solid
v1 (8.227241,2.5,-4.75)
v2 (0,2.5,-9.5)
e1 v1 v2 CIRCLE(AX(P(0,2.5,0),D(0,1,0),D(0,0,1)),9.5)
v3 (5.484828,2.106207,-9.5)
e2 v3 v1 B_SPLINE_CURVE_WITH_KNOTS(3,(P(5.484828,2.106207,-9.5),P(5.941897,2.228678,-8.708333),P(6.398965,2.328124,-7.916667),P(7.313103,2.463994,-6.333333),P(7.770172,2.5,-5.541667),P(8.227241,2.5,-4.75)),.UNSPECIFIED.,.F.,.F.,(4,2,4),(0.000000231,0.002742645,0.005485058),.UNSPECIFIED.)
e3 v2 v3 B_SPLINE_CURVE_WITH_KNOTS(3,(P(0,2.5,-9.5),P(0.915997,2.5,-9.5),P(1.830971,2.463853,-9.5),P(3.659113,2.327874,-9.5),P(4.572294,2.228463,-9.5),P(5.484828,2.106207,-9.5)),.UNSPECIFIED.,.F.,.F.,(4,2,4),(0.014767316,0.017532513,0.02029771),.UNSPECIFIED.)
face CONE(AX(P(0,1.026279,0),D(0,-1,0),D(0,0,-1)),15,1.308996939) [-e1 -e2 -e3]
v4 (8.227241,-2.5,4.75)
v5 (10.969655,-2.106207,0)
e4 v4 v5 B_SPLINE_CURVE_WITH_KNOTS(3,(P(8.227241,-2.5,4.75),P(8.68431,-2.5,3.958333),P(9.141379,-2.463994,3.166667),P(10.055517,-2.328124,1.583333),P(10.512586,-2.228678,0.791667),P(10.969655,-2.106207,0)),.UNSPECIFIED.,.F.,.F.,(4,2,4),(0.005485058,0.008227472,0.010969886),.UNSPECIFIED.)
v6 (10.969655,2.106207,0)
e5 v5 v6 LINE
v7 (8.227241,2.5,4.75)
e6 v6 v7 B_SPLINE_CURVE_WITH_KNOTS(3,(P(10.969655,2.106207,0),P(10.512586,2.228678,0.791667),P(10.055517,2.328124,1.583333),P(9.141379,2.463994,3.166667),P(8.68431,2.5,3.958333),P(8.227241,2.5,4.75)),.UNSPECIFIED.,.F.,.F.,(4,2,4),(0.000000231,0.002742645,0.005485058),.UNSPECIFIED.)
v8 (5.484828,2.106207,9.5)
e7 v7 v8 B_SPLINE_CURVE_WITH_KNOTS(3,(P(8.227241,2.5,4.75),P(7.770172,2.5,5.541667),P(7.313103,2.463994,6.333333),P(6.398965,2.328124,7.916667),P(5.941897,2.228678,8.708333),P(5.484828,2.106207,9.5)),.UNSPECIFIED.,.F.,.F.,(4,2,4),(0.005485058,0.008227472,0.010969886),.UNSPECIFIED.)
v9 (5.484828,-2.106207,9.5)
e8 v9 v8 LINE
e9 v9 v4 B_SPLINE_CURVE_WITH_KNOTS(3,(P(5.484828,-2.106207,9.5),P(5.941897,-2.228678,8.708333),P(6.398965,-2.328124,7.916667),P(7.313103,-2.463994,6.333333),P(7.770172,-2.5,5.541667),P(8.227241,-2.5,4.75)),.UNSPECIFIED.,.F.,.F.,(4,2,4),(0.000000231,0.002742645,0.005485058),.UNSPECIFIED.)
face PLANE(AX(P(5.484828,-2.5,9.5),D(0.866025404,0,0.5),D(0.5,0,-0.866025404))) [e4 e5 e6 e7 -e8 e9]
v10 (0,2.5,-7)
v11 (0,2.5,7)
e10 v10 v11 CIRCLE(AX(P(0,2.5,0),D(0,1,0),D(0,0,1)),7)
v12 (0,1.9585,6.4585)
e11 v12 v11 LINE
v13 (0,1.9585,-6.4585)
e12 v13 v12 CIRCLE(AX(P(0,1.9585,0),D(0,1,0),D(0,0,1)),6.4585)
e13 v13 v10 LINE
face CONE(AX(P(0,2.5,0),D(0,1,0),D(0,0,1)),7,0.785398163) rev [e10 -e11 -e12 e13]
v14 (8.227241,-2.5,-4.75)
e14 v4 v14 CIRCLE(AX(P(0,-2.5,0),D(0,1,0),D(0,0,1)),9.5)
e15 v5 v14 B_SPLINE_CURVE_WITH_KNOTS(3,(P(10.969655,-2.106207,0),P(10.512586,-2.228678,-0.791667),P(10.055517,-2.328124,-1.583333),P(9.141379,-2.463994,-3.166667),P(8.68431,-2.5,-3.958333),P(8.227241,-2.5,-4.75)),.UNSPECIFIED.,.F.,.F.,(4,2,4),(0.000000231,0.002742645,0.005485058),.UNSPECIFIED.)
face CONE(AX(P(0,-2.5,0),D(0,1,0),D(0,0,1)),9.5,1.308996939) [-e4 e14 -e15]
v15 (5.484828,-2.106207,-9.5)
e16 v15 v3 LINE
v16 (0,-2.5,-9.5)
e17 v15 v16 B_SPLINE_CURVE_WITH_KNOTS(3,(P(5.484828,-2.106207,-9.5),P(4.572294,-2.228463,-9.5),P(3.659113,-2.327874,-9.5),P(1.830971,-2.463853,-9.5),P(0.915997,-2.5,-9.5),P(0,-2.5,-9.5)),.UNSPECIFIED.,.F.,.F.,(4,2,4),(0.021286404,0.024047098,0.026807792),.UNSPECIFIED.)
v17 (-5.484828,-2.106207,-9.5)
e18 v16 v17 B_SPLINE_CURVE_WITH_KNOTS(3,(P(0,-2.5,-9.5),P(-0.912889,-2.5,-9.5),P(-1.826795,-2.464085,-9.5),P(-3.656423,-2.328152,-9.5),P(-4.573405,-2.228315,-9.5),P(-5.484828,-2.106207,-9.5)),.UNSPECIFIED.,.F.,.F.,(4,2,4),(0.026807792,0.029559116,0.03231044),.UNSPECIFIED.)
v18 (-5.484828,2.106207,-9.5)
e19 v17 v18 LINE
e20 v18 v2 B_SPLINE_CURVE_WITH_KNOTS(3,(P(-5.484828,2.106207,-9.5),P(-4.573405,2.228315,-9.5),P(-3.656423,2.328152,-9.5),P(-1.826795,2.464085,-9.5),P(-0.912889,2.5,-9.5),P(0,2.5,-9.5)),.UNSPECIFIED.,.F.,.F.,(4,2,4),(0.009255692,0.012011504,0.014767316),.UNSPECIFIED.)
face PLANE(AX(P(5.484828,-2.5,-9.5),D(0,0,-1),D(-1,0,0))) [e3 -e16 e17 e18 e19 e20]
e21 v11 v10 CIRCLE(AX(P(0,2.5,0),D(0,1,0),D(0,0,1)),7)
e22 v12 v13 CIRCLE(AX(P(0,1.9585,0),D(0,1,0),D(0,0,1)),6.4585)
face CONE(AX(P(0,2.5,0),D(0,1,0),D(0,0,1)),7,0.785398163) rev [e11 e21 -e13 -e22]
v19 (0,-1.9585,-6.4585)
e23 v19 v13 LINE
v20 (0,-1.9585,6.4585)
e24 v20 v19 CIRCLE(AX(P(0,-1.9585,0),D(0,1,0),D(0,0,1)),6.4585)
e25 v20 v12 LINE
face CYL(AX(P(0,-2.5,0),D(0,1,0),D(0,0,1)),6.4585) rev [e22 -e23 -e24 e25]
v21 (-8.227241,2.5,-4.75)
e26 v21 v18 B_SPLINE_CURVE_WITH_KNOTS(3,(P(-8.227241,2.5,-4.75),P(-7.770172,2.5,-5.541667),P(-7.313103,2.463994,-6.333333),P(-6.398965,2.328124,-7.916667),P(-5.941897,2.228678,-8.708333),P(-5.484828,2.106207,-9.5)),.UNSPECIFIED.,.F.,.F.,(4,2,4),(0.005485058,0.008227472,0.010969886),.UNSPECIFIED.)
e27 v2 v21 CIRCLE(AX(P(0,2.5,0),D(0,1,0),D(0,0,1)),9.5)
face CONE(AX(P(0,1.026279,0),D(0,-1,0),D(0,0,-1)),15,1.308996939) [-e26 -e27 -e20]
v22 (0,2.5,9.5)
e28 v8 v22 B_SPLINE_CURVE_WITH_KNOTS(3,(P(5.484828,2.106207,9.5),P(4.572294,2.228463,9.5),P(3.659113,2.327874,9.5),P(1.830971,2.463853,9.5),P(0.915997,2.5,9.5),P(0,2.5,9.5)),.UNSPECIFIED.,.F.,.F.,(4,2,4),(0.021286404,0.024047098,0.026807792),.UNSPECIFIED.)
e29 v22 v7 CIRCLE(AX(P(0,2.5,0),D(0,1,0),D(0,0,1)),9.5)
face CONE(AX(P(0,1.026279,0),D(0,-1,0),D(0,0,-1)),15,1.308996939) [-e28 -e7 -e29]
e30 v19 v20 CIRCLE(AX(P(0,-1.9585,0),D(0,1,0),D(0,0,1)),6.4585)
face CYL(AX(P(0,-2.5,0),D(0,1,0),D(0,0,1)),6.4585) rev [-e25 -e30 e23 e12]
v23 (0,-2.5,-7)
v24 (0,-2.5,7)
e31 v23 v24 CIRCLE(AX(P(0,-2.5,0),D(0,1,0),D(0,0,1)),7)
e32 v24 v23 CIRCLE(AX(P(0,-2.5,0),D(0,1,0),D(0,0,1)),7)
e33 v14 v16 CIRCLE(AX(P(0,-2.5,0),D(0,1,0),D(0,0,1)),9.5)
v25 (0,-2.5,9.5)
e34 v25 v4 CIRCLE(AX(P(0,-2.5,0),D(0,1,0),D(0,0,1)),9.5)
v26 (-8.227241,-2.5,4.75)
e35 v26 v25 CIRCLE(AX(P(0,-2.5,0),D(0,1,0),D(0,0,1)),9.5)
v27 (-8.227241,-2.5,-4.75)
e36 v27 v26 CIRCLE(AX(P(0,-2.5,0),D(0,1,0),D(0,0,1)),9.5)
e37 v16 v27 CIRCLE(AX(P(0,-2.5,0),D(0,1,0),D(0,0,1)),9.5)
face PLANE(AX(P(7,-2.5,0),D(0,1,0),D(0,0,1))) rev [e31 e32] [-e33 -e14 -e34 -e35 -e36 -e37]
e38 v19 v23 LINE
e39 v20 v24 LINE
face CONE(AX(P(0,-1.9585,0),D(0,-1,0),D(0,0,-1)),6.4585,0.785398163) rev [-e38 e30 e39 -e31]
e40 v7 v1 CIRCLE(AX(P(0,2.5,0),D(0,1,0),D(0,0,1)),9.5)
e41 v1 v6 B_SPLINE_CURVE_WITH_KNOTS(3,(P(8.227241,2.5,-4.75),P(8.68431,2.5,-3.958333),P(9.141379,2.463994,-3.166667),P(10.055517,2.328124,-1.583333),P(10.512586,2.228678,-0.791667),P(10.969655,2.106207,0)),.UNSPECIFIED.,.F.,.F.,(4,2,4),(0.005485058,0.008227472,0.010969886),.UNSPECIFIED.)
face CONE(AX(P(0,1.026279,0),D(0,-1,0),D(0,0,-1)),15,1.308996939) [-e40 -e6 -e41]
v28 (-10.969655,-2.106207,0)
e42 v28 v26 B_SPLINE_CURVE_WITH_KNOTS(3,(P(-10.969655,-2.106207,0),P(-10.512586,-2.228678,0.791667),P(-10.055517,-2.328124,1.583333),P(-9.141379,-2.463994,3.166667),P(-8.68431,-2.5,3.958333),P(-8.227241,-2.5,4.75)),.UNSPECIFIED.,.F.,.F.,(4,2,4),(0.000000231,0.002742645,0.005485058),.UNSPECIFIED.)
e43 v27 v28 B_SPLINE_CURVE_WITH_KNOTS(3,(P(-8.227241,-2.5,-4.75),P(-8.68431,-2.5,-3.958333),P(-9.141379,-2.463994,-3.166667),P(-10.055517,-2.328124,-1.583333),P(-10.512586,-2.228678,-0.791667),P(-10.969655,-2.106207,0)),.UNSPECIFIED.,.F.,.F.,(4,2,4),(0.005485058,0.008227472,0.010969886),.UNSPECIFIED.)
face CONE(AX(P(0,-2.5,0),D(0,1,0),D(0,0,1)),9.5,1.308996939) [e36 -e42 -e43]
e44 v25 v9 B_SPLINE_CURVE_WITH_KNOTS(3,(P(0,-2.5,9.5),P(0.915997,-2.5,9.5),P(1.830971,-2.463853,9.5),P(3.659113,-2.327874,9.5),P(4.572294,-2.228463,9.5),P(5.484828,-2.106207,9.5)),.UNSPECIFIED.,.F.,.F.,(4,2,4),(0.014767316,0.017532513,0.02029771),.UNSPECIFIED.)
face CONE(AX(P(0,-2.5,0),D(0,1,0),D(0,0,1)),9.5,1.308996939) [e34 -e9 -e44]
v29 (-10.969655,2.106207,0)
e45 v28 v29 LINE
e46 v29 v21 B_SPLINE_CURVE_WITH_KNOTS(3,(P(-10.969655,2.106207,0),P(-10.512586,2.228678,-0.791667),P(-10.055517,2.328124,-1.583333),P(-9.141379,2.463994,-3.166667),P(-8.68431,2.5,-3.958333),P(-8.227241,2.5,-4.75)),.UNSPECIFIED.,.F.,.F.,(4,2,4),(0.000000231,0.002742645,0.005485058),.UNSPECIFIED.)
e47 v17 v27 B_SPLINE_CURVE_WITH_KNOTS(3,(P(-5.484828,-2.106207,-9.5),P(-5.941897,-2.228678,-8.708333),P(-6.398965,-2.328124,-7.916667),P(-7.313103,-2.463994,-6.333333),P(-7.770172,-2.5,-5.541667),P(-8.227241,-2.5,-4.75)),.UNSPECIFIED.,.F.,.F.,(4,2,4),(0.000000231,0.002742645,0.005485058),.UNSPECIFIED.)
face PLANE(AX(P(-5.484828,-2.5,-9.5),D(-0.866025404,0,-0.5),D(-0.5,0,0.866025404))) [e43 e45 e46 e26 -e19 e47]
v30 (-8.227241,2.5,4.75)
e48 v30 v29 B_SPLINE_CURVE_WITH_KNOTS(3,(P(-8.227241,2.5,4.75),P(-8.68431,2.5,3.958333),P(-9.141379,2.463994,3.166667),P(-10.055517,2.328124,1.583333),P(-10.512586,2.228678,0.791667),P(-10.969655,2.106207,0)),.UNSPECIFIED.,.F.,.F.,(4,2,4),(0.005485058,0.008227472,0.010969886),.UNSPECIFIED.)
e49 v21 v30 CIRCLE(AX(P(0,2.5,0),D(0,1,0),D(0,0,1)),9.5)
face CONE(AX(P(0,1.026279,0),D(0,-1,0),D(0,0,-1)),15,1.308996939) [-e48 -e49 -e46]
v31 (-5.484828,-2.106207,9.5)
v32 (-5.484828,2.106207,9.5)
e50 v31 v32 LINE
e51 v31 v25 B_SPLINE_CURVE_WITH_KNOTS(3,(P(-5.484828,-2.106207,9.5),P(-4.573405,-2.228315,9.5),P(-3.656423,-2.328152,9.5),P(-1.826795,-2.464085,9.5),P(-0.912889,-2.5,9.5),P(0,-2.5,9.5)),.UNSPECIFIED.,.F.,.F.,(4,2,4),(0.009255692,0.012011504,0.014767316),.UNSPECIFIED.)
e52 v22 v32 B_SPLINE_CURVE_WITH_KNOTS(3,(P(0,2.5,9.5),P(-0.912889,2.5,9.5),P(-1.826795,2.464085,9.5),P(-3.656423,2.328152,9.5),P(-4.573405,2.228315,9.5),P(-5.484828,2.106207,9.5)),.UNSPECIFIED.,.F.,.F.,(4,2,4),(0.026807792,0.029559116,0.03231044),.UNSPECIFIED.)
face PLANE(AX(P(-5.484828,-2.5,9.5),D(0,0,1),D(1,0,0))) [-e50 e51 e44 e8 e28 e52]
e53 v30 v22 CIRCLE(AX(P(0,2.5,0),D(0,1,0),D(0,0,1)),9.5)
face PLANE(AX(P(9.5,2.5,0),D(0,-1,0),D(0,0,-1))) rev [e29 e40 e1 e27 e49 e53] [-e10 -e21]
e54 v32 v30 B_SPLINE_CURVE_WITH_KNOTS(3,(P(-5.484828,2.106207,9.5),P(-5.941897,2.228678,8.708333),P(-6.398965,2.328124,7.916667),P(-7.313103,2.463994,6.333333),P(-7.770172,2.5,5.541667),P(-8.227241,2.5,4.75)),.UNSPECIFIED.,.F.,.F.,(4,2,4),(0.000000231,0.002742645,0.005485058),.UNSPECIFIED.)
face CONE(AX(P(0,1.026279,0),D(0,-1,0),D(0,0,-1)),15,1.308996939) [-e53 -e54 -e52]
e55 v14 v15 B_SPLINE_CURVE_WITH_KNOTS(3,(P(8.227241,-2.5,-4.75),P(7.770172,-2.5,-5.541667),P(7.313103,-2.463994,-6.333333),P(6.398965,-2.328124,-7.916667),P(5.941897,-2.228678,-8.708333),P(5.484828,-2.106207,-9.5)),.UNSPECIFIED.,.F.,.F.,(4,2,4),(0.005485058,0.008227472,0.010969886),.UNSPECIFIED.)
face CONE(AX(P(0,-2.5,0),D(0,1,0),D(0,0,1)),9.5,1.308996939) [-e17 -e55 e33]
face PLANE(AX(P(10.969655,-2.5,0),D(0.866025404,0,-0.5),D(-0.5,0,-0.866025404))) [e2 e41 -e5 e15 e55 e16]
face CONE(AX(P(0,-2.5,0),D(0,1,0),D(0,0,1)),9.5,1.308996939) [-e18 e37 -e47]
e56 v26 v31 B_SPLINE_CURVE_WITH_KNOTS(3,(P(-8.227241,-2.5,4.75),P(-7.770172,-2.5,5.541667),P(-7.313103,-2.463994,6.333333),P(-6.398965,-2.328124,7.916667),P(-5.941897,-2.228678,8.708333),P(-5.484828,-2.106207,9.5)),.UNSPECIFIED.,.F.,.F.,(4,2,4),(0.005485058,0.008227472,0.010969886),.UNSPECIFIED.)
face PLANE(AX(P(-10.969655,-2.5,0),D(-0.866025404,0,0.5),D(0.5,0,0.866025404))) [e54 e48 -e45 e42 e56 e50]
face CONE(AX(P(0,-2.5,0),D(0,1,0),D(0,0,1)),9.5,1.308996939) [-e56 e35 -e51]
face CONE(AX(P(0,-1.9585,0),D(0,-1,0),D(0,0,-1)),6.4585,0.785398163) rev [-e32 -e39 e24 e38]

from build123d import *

# Parameters (mm, degrees)
CUT_EXTRUDE1_DEPTH      = 2.5
CUT_EXTRUDE1_DEPTH_BACK = 2.5
SKETCH2_R               = 20


with BuildPart() as part:
    # Sketch1 → Revolve1 (revolve)
    with BuildSketch(Plane.XY, mode=Mode.PRIVATE) as revolve1_sk:
        Polygon((6.4585, -1.9585), (7, -2.5), (9.5, -2.5), (15, -1.026279442), (15, 1.026279442), (9.5, 2.5), (7, 2.5), (6.4585, 1.9585), align=None)
    revolve(revolve1_sk.sketch.rotate(Axis((0, -2.5, 0), (0, 1, 0)), 270), axis=Axis((0, -2.5, 0), (0, 1, 0)))

    # Sketch2 → Cut-Extrude1 (cut, two sides: drawn at the far end of the back side and taken through both)
    with BuildSketch(Plane(origin=(0, 0, 0), x_dir=(1, 0, 0), z_dir=(0, 1, 0)).offset(-CUT_EXTRUDE1_DEPTH_BACK)):
        Circle(SKETCH2_R)
        Polygon((-10.969655115, 0), (-5.484827557, -9.5), (5.484827557, -9.5), (10.969655115, 0), (5.484827557, 9.5), (-5.484827557, 9.5), align=None, mode=Mode.SUBTRACT)
    extrude(amount=CUT_EXTRUDE1_DEPTH + CUT_EXTRUDE1_DEPTH_BACK, mode=Mode.SUBTRACT)


solid = part.part
